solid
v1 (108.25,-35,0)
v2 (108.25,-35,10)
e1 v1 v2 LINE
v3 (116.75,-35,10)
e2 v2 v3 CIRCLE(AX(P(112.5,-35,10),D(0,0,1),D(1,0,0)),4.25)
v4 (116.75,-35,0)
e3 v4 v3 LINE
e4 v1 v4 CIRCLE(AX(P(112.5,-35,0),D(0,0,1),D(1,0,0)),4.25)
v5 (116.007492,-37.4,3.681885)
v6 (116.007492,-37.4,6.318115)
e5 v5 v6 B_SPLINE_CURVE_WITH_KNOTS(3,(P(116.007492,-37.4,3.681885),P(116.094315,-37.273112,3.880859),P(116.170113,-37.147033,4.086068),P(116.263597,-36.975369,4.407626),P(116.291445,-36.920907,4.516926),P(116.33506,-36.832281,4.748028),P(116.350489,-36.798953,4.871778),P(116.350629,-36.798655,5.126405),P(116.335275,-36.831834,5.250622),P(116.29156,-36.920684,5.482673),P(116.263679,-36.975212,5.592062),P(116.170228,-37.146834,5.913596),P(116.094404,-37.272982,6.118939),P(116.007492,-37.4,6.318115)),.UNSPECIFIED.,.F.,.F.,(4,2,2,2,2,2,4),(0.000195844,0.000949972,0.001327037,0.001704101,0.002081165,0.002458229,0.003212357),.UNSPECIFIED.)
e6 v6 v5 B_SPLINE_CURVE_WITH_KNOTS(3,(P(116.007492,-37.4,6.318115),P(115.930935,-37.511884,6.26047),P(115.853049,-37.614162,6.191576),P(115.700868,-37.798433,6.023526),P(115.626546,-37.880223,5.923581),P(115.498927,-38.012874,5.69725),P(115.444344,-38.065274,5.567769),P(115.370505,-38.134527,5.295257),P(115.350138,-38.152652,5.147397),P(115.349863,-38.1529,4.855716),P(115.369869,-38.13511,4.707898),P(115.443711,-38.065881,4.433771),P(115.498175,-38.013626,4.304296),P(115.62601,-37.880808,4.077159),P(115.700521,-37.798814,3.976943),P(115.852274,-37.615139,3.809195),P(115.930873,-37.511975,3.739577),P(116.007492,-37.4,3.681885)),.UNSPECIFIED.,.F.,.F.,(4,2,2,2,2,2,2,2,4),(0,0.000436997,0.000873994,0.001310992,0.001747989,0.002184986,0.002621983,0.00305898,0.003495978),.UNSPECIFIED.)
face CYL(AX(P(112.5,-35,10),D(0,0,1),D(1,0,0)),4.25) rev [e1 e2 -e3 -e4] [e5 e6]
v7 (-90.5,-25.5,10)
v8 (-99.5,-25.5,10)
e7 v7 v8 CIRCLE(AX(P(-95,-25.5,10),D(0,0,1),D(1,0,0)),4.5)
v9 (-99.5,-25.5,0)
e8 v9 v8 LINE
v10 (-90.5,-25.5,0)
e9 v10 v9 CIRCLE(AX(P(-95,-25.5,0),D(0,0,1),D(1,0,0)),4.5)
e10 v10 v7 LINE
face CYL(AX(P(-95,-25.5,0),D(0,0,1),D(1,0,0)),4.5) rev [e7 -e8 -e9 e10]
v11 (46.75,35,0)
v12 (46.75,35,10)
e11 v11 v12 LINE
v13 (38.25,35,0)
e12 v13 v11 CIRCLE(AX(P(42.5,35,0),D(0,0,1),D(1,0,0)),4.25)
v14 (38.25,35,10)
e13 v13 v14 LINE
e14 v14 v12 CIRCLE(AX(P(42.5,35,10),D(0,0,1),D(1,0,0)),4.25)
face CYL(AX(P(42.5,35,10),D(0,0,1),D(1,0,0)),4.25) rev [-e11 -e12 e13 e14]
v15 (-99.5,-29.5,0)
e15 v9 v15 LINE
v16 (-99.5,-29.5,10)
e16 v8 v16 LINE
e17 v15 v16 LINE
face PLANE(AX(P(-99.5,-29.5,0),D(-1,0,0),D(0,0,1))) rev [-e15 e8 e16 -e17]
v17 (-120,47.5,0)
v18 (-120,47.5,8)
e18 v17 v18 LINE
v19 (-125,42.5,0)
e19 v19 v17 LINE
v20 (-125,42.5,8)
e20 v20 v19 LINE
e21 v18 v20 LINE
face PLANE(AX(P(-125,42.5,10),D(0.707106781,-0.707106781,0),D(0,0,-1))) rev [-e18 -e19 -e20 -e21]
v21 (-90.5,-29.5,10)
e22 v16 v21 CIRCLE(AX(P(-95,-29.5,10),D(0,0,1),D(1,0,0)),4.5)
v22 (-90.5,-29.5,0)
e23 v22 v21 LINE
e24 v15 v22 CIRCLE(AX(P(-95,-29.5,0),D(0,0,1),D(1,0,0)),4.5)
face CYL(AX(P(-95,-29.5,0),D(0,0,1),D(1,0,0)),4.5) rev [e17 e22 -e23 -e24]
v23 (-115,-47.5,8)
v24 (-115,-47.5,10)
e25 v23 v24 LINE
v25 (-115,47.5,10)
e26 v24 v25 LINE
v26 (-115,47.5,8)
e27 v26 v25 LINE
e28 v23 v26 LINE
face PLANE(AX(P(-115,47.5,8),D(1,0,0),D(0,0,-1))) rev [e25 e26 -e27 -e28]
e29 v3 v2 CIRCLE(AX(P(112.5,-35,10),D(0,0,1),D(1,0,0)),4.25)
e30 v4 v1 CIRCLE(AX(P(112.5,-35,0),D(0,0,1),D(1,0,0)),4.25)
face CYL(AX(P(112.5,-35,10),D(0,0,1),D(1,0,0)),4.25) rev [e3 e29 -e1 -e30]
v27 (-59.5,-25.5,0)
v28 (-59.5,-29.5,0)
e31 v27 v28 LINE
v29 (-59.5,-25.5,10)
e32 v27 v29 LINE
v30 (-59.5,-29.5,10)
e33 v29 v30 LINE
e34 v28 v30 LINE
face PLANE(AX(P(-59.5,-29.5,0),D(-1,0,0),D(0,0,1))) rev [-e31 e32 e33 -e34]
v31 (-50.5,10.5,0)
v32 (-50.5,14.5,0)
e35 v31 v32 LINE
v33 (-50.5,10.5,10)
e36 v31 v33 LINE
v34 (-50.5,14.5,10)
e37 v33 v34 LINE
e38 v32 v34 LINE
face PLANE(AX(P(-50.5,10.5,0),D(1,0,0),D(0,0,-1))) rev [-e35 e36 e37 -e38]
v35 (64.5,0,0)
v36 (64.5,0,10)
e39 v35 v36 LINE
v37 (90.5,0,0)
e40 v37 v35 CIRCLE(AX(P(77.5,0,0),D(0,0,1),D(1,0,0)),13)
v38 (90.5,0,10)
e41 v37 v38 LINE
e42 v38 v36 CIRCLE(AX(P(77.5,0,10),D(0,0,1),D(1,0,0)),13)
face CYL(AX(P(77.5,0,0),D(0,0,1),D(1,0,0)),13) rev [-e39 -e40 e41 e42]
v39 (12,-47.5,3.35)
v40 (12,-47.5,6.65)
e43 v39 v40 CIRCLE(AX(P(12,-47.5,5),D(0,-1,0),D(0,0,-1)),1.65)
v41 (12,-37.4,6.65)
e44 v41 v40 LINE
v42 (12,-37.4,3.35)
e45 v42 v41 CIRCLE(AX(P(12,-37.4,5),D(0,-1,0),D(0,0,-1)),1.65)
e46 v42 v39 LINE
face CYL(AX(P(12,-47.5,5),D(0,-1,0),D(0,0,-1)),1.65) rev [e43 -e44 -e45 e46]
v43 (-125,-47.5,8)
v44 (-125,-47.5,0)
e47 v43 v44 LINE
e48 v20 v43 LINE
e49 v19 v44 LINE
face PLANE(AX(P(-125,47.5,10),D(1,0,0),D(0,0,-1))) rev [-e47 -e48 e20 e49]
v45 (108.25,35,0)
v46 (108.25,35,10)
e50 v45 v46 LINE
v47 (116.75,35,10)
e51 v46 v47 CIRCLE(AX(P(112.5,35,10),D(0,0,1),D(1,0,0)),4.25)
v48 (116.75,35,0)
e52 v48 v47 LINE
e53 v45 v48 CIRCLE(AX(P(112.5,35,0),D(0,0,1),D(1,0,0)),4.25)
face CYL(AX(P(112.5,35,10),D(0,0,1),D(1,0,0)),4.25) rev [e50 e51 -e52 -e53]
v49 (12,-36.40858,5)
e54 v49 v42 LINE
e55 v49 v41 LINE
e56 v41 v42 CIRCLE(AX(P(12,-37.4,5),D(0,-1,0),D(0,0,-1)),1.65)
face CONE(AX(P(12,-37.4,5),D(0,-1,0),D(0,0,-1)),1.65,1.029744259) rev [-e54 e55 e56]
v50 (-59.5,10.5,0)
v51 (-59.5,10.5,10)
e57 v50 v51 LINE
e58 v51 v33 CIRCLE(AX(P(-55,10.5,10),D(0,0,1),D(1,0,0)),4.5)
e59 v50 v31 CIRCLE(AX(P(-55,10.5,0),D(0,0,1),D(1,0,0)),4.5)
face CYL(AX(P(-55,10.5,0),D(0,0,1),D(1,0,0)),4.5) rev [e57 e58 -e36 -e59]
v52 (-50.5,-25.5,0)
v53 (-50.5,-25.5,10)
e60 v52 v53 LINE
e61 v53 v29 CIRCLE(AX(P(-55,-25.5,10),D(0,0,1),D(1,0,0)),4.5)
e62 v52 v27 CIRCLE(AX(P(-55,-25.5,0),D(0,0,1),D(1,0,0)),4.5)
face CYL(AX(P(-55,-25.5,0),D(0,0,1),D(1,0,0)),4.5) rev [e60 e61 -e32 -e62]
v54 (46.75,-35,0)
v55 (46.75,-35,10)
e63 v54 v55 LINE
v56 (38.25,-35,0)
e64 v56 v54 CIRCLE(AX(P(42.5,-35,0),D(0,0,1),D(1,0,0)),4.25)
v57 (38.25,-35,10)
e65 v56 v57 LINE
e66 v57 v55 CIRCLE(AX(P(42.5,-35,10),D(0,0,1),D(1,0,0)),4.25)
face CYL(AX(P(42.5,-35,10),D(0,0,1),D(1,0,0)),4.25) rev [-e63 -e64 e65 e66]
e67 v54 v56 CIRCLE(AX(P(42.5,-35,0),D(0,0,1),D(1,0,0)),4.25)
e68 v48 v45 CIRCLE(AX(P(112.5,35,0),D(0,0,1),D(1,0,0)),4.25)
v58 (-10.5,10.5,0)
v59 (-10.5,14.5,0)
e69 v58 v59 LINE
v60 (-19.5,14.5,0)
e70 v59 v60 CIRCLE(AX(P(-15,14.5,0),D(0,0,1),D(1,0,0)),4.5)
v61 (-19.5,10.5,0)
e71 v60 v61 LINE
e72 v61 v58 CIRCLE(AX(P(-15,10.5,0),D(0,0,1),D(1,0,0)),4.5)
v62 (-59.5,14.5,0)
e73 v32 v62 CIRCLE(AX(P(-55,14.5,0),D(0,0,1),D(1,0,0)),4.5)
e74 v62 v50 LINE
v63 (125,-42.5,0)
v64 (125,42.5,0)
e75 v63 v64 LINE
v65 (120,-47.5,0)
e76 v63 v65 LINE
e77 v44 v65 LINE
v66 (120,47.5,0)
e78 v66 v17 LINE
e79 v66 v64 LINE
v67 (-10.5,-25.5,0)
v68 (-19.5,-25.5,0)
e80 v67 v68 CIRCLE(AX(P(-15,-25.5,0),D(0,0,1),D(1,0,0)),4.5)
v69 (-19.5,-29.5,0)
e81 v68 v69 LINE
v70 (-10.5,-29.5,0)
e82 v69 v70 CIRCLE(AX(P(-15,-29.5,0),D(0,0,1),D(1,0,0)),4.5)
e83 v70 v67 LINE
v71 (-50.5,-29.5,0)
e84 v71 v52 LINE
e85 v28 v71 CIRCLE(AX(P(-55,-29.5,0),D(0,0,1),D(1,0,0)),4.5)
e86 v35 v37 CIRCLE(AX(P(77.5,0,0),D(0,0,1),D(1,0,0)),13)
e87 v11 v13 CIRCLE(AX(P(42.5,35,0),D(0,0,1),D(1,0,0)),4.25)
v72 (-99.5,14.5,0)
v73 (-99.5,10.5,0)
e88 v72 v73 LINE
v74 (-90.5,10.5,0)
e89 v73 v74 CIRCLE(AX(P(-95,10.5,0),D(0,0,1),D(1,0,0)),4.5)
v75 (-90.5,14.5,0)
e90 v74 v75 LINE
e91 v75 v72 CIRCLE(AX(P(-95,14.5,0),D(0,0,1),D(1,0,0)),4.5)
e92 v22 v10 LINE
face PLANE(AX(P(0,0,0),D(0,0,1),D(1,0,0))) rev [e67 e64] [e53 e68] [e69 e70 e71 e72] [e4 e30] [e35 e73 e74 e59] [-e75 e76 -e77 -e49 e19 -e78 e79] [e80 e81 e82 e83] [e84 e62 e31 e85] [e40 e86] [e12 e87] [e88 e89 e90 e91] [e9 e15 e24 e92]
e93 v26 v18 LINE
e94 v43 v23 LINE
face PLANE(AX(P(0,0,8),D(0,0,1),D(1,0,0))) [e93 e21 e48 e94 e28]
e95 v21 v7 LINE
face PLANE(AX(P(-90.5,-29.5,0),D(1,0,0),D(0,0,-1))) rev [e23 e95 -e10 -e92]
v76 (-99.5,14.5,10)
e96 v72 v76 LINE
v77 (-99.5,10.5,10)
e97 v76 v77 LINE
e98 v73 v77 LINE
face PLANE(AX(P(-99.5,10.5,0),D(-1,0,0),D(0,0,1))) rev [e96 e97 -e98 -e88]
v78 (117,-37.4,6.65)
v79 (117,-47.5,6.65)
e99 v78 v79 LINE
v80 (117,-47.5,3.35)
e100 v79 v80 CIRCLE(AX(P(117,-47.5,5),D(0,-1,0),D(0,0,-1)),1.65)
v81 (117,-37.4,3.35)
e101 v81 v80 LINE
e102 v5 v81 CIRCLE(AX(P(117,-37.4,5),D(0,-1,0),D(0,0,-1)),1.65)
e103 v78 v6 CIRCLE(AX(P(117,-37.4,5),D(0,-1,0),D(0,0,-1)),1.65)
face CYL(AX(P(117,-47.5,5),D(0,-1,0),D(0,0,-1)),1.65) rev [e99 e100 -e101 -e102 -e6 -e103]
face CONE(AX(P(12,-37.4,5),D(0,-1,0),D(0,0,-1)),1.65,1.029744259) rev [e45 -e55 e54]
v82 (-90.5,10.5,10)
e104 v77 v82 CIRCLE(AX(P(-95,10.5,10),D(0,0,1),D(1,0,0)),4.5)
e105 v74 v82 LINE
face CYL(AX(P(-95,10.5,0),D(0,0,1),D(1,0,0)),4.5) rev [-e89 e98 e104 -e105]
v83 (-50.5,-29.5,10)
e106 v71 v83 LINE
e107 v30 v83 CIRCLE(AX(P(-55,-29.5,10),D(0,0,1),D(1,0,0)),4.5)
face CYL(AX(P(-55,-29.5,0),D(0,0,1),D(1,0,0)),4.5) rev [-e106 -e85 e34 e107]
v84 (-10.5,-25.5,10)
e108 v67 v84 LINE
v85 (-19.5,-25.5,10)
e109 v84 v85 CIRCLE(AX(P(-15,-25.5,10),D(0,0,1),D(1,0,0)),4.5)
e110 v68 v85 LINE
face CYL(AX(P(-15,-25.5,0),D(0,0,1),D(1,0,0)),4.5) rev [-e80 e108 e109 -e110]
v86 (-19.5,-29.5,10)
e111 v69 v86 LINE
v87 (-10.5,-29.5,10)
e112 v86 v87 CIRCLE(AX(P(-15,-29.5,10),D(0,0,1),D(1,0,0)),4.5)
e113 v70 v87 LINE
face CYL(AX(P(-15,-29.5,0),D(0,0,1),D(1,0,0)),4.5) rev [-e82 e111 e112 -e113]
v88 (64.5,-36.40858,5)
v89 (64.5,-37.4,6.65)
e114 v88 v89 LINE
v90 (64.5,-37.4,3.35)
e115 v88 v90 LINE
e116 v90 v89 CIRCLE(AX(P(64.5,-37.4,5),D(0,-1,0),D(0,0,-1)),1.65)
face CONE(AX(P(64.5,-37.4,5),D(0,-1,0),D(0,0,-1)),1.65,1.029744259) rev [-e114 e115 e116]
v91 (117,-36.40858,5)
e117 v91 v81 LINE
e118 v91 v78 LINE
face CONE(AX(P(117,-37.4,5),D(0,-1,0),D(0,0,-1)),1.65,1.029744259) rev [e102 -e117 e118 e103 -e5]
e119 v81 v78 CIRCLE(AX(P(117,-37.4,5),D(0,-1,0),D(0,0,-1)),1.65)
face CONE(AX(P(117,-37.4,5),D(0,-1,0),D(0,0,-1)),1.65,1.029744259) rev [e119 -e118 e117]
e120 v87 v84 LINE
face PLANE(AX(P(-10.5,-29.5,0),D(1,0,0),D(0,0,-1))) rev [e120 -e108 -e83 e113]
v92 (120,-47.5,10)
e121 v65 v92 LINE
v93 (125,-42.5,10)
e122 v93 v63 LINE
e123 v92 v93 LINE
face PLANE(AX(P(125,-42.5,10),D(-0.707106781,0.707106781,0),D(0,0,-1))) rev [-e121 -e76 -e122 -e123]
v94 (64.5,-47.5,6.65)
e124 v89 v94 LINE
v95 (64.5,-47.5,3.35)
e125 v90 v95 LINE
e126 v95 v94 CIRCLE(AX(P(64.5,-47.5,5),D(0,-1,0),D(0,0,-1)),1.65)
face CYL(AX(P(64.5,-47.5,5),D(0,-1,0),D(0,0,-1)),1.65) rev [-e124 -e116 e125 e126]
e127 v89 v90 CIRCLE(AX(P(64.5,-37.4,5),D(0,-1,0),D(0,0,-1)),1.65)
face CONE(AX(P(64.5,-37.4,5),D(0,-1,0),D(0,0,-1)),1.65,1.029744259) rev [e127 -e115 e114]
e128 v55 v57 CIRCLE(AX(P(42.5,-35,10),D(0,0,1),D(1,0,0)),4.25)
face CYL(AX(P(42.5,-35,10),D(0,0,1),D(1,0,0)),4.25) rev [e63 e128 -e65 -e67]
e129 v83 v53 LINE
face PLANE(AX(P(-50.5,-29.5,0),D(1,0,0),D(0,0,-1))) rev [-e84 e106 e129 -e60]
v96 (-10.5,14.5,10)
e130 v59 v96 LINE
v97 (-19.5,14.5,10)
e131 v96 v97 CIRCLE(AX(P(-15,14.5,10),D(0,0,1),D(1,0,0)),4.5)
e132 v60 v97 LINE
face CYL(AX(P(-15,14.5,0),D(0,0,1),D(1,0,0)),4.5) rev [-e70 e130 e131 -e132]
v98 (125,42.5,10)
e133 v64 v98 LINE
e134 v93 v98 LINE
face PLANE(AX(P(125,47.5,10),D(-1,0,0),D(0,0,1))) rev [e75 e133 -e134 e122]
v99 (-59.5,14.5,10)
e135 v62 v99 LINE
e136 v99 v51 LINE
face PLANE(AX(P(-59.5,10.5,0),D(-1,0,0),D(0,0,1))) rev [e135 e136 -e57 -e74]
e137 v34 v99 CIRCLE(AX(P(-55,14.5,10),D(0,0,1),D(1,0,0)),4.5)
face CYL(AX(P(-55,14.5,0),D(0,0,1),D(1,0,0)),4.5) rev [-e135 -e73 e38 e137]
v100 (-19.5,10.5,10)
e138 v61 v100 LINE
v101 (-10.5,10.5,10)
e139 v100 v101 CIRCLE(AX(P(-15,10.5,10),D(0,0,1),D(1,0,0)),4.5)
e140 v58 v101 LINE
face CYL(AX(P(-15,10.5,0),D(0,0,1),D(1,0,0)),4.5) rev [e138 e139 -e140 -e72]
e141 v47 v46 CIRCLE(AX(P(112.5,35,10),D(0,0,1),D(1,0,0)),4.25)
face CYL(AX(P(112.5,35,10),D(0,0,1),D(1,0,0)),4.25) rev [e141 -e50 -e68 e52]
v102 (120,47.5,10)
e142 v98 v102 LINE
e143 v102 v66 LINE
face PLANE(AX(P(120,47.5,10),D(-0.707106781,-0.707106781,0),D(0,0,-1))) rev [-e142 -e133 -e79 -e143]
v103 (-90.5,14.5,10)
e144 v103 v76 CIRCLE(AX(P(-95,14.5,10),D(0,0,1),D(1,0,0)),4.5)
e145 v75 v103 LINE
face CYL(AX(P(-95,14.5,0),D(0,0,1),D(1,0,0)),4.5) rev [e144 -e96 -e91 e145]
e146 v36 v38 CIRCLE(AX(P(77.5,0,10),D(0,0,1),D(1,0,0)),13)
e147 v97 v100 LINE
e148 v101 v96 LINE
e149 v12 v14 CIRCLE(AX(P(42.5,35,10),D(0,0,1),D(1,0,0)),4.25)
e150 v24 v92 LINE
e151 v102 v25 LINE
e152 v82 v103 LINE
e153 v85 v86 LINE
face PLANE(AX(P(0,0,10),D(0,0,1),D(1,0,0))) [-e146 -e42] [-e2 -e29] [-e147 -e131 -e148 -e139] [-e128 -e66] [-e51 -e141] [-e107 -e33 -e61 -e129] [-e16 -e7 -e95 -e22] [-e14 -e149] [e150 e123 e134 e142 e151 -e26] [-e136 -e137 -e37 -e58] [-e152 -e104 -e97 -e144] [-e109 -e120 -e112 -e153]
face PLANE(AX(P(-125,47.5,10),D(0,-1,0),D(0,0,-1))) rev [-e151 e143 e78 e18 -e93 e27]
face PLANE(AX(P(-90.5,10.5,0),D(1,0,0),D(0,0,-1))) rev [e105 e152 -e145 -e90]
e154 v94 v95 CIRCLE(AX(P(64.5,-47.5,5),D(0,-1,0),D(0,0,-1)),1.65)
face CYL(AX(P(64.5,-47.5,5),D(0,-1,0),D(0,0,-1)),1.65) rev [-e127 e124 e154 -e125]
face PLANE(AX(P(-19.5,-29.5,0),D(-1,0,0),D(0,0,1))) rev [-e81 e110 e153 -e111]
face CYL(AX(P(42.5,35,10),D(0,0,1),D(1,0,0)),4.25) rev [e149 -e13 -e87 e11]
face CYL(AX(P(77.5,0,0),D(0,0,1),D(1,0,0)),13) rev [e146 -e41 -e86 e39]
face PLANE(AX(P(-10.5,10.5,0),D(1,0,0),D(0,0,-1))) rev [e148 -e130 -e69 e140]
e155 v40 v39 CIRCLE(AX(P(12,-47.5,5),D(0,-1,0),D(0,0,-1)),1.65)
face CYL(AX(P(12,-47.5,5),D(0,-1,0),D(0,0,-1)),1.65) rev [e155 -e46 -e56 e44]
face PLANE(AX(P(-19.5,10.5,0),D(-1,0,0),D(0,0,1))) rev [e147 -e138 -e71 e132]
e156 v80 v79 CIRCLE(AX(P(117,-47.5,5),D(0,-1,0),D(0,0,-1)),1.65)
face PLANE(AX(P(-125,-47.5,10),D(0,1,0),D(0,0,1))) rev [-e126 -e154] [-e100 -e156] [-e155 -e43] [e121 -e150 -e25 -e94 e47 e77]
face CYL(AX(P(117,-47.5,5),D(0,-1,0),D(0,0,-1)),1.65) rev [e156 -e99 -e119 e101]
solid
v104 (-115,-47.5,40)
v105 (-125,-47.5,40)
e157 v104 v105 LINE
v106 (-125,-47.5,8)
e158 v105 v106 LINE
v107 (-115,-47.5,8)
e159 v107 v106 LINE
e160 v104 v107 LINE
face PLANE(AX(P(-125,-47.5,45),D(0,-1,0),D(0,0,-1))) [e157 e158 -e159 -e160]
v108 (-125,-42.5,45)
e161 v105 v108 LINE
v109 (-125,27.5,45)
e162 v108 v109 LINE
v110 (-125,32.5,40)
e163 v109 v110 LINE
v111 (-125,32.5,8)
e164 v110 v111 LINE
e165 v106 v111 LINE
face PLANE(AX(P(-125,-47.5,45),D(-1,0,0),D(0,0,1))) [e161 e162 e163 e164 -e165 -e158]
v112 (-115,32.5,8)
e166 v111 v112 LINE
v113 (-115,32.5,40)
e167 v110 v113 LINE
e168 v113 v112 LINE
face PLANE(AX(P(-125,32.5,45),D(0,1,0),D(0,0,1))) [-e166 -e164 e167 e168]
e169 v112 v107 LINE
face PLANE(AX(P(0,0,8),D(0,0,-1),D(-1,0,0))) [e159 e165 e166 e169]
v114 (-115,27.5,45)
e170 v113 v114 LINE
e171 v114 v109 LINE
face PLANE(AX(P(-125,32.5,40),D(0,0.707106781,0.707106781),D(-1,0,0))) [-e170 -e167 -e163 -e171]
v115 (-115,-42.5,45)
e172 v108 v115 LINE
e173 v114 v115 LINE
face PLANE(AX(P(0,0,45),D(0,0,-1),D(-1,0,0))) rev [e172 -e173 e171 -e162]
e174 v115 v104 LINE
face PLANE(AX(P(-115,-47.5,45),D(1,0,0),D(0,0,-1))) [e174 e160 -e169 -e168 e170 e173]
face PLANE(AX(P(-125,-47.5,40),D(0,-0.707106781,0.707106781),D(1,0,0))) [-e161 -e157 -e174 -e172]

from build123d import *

# Parameters (mm, degrees)
SKETCH_1_W                  = 250
SKETCH_1_H                  = 95
EXTRUDE_1_DEPTH             = 10
CUT_EXTRUDE_2_DEPTH         = 135.094183319
PATTERN_LINEAR_1_COUNT      = 2
PATTERN_LINEAR_1_PITCH      = 40
PATTERN_LINEAR_1_COUNT_DIR2 = 2
PATTERN_LINEAR_1_PITCH_DIR2 = 40
PATTERN_LINEAR_2_COUNT      = 2
PATTERN_LINEAR_2_PITCH      = 40
PATTERN_LINEAR_2_COUNT_DIR2 = 2
PATTERN_LINEAR_2_PITCH_DIR2 = 40
HOLE_WIZARD_M10_3_D         = 8.5
HOLE_WIZARD_M10_3_DEPTH     = 24.5
HOLE_WIZARD_M10_3_TIP       = 2.553657631
SKETCH_12_R                 = 13
CUT_EXTRUDE_5_DEPTH         = 135.094183319
HOLE_WIZARD_M4_1_D          = 3.3
HOLE_WIZARD_M4_1_DEPTH      = 10.1
HOLE_WIZARD_M4_1_TIP        = 0.991420021
SKETCH_22_W                 = 10
SKETCH_22_H                 = 95
CUT_EXTRUDE_6_DEPTH         = 2
SKETCH_21_W                 = 10
SKETCH_21_H                 = 80
EXTRUDE_2_DEPTH             = 37
CHAMFER_1_SIZE              = 5
CHAMFER_2_SIZE              = 5


with BuildPart() as part:
    # 草图1 → 凸台-拉伸1 (new body)
    with BuildSketch(Plane.XY):
        Rectangle(SKETCH_1_W, SKETCH_1_H)
    extrude(amount=EXTRUDE_1_DEPTH)

    # 草图3 → 切除-拉伸2 (cut, through all)
    with BuildSketch(Plane.XY.offset(10)):
        with BuildLine():
            Line((-59.5, -29.5), (-59.5, -25.5))
            ThreePointArc((-59.5, -25.5), (-55, -21), (-50.5, -25.5))
            Line((-50.5, -25.5), (-50.5, -29.5))
            ThreePointArc((-50.5, -29.5), (-55, -34), (-59.5, -29.5))
        make_face()
    cut_extrude_2 = extrude(amount=-CUT_EXTRUDE_2_DEPTH, mode=Mode.SUBTRACT)

    # 阵列(线性)1: Cut-Extrude 2 2 × 2
    with Locations(*[(i * PATTERN_LINEAR_1_PITCH, j * PATTERN_LINEAR_1_PITCH_DIR2, 0) for i in range(PATTERN_LINEAR_1_COUNT) for j in range(PATTERN_LINEAR_1_COUNT_DIR2) if (i, j) != (0, 0)]):
        add(cut_extrude_2, mode=Mode.SUBTRACT)

    # 阵列(线性)2: Cut-Extrude 2 2 × 2
    with Locations(*[(-i * PATTERN_LINEAR_2_PITCH, j * PATTERN_LINEAR_2_PITCH_DIR2, 0) for i in range(PATTERN_LINEAR_2_COUNT) for j in range(PATTERN_LINEAR_2_COUNT_DIR2) if (i, j) != (0, 0)]):
        add(cut_extrude_2, mode=Mode.SUBTRACT)

    # M10 螺纹孔3
    with Locations(Plane(origin=(42.5, 35, 10), x_dir=(1, 0, 0), z_dir=(0, 0, 1))):
        with Locations((0, 0), (70, 0), (70, -70), (0, -70)):
            Hole(HOLE_WIZARD_M10_3_D / 2, depth=HOLE_WIZARD_M10_3_DEPTH)
            with Locations((0, 0, -(HOLE_WIZARD_M10_3_DEPTH + HOLE_WIZARD_M10_3_TIP / 2))):  # 118° drill point
                Cone(0, HOLE_WIZARD_M10_3_D / 2, HOLE_WIZARD_M10_3_TIP, mode=Mode.SUBTRACT)

    # 草图12 → 切除-拉伸5 (cut, through all)
    with BuildSketch(Plane.XY.offset(10)):
        with Locations((77.5, 0)):
            Circle(SKETCH_12_R)
    extrude(amount=-CUT_EXTRUDE_5_DEPTH, mode=Mode.SUBTRACT)

    # M4 螺纹孔1
    with Locations(Plane(origin=(117, -47.5, 5), x_dir=(0, 0, -1), z_dir=(0, -1, 0))):
        with Locations((0, 0), (0, -105), (0, -52.5)):
            Hole(HOLE_WIZARD_M4_1_D / 2, depth=HOLE_WIZARD_M4_1_DEPTH)
            with Locations((0, 0, -(HOLE_WIZARD_M4_1_DEPTH + HOLE_WIZARD_M4_1_TIP / 2))):  # 118° drill point
                Cone(0, HOLE_WIZARD_M4_1_D / 2, HOLE_WIZARD_M4_1_TIP, mode=Mode.SUBTRACT)

    # 草图22 → 切除-拉伸6 (cut)
    with BuildSketch(Plane.XY.offset(10)):
        with Locations((-120, 0)):
            Rectangle(SKETCH_22_W, SKETCH_22_H)
    extrude(amount=-CUT_EXTRUDE_6_DEPTH, mode=Mode.SUBTRACT)

    # 倒角1
    chamfer_1_edges = [part.edges().sort_by_distance(p)[0] for p in [
        (-125, 47.5, 4),
        (125, -47.5, 5),
        (125, 47.5, 5),
    ]]
    chamfer(chamfer_1_edges, length=CHAMFER_1_SIZE)


with BuildPart() as body_2:
    # 草图21 → 凸台-拉伸2 (new body)
    with BuildSketch(Plane(origin=(0, 0, 8), x_dir=(-1, 0, 0), z_dir=(0, 0, -1))):
        with Locations((120, -7.5)):
            Rectangle(SKETCH_21_W, SKETCH_21_H)
    extrude(amount=-EXTRUDE_2_DEPTH)

    # 倒角2
    chamfer_2_edges = [body_2.edges().sort_by_distance(p)[0] for p in [
        (-120, -47.5, 45),
        (-120, 32.5, 45),
    ]]
    chamfer(chamfer_2_edges, length=CHAMFER_2_SIZE)


solid = Compound([part.part, body_2.part])
